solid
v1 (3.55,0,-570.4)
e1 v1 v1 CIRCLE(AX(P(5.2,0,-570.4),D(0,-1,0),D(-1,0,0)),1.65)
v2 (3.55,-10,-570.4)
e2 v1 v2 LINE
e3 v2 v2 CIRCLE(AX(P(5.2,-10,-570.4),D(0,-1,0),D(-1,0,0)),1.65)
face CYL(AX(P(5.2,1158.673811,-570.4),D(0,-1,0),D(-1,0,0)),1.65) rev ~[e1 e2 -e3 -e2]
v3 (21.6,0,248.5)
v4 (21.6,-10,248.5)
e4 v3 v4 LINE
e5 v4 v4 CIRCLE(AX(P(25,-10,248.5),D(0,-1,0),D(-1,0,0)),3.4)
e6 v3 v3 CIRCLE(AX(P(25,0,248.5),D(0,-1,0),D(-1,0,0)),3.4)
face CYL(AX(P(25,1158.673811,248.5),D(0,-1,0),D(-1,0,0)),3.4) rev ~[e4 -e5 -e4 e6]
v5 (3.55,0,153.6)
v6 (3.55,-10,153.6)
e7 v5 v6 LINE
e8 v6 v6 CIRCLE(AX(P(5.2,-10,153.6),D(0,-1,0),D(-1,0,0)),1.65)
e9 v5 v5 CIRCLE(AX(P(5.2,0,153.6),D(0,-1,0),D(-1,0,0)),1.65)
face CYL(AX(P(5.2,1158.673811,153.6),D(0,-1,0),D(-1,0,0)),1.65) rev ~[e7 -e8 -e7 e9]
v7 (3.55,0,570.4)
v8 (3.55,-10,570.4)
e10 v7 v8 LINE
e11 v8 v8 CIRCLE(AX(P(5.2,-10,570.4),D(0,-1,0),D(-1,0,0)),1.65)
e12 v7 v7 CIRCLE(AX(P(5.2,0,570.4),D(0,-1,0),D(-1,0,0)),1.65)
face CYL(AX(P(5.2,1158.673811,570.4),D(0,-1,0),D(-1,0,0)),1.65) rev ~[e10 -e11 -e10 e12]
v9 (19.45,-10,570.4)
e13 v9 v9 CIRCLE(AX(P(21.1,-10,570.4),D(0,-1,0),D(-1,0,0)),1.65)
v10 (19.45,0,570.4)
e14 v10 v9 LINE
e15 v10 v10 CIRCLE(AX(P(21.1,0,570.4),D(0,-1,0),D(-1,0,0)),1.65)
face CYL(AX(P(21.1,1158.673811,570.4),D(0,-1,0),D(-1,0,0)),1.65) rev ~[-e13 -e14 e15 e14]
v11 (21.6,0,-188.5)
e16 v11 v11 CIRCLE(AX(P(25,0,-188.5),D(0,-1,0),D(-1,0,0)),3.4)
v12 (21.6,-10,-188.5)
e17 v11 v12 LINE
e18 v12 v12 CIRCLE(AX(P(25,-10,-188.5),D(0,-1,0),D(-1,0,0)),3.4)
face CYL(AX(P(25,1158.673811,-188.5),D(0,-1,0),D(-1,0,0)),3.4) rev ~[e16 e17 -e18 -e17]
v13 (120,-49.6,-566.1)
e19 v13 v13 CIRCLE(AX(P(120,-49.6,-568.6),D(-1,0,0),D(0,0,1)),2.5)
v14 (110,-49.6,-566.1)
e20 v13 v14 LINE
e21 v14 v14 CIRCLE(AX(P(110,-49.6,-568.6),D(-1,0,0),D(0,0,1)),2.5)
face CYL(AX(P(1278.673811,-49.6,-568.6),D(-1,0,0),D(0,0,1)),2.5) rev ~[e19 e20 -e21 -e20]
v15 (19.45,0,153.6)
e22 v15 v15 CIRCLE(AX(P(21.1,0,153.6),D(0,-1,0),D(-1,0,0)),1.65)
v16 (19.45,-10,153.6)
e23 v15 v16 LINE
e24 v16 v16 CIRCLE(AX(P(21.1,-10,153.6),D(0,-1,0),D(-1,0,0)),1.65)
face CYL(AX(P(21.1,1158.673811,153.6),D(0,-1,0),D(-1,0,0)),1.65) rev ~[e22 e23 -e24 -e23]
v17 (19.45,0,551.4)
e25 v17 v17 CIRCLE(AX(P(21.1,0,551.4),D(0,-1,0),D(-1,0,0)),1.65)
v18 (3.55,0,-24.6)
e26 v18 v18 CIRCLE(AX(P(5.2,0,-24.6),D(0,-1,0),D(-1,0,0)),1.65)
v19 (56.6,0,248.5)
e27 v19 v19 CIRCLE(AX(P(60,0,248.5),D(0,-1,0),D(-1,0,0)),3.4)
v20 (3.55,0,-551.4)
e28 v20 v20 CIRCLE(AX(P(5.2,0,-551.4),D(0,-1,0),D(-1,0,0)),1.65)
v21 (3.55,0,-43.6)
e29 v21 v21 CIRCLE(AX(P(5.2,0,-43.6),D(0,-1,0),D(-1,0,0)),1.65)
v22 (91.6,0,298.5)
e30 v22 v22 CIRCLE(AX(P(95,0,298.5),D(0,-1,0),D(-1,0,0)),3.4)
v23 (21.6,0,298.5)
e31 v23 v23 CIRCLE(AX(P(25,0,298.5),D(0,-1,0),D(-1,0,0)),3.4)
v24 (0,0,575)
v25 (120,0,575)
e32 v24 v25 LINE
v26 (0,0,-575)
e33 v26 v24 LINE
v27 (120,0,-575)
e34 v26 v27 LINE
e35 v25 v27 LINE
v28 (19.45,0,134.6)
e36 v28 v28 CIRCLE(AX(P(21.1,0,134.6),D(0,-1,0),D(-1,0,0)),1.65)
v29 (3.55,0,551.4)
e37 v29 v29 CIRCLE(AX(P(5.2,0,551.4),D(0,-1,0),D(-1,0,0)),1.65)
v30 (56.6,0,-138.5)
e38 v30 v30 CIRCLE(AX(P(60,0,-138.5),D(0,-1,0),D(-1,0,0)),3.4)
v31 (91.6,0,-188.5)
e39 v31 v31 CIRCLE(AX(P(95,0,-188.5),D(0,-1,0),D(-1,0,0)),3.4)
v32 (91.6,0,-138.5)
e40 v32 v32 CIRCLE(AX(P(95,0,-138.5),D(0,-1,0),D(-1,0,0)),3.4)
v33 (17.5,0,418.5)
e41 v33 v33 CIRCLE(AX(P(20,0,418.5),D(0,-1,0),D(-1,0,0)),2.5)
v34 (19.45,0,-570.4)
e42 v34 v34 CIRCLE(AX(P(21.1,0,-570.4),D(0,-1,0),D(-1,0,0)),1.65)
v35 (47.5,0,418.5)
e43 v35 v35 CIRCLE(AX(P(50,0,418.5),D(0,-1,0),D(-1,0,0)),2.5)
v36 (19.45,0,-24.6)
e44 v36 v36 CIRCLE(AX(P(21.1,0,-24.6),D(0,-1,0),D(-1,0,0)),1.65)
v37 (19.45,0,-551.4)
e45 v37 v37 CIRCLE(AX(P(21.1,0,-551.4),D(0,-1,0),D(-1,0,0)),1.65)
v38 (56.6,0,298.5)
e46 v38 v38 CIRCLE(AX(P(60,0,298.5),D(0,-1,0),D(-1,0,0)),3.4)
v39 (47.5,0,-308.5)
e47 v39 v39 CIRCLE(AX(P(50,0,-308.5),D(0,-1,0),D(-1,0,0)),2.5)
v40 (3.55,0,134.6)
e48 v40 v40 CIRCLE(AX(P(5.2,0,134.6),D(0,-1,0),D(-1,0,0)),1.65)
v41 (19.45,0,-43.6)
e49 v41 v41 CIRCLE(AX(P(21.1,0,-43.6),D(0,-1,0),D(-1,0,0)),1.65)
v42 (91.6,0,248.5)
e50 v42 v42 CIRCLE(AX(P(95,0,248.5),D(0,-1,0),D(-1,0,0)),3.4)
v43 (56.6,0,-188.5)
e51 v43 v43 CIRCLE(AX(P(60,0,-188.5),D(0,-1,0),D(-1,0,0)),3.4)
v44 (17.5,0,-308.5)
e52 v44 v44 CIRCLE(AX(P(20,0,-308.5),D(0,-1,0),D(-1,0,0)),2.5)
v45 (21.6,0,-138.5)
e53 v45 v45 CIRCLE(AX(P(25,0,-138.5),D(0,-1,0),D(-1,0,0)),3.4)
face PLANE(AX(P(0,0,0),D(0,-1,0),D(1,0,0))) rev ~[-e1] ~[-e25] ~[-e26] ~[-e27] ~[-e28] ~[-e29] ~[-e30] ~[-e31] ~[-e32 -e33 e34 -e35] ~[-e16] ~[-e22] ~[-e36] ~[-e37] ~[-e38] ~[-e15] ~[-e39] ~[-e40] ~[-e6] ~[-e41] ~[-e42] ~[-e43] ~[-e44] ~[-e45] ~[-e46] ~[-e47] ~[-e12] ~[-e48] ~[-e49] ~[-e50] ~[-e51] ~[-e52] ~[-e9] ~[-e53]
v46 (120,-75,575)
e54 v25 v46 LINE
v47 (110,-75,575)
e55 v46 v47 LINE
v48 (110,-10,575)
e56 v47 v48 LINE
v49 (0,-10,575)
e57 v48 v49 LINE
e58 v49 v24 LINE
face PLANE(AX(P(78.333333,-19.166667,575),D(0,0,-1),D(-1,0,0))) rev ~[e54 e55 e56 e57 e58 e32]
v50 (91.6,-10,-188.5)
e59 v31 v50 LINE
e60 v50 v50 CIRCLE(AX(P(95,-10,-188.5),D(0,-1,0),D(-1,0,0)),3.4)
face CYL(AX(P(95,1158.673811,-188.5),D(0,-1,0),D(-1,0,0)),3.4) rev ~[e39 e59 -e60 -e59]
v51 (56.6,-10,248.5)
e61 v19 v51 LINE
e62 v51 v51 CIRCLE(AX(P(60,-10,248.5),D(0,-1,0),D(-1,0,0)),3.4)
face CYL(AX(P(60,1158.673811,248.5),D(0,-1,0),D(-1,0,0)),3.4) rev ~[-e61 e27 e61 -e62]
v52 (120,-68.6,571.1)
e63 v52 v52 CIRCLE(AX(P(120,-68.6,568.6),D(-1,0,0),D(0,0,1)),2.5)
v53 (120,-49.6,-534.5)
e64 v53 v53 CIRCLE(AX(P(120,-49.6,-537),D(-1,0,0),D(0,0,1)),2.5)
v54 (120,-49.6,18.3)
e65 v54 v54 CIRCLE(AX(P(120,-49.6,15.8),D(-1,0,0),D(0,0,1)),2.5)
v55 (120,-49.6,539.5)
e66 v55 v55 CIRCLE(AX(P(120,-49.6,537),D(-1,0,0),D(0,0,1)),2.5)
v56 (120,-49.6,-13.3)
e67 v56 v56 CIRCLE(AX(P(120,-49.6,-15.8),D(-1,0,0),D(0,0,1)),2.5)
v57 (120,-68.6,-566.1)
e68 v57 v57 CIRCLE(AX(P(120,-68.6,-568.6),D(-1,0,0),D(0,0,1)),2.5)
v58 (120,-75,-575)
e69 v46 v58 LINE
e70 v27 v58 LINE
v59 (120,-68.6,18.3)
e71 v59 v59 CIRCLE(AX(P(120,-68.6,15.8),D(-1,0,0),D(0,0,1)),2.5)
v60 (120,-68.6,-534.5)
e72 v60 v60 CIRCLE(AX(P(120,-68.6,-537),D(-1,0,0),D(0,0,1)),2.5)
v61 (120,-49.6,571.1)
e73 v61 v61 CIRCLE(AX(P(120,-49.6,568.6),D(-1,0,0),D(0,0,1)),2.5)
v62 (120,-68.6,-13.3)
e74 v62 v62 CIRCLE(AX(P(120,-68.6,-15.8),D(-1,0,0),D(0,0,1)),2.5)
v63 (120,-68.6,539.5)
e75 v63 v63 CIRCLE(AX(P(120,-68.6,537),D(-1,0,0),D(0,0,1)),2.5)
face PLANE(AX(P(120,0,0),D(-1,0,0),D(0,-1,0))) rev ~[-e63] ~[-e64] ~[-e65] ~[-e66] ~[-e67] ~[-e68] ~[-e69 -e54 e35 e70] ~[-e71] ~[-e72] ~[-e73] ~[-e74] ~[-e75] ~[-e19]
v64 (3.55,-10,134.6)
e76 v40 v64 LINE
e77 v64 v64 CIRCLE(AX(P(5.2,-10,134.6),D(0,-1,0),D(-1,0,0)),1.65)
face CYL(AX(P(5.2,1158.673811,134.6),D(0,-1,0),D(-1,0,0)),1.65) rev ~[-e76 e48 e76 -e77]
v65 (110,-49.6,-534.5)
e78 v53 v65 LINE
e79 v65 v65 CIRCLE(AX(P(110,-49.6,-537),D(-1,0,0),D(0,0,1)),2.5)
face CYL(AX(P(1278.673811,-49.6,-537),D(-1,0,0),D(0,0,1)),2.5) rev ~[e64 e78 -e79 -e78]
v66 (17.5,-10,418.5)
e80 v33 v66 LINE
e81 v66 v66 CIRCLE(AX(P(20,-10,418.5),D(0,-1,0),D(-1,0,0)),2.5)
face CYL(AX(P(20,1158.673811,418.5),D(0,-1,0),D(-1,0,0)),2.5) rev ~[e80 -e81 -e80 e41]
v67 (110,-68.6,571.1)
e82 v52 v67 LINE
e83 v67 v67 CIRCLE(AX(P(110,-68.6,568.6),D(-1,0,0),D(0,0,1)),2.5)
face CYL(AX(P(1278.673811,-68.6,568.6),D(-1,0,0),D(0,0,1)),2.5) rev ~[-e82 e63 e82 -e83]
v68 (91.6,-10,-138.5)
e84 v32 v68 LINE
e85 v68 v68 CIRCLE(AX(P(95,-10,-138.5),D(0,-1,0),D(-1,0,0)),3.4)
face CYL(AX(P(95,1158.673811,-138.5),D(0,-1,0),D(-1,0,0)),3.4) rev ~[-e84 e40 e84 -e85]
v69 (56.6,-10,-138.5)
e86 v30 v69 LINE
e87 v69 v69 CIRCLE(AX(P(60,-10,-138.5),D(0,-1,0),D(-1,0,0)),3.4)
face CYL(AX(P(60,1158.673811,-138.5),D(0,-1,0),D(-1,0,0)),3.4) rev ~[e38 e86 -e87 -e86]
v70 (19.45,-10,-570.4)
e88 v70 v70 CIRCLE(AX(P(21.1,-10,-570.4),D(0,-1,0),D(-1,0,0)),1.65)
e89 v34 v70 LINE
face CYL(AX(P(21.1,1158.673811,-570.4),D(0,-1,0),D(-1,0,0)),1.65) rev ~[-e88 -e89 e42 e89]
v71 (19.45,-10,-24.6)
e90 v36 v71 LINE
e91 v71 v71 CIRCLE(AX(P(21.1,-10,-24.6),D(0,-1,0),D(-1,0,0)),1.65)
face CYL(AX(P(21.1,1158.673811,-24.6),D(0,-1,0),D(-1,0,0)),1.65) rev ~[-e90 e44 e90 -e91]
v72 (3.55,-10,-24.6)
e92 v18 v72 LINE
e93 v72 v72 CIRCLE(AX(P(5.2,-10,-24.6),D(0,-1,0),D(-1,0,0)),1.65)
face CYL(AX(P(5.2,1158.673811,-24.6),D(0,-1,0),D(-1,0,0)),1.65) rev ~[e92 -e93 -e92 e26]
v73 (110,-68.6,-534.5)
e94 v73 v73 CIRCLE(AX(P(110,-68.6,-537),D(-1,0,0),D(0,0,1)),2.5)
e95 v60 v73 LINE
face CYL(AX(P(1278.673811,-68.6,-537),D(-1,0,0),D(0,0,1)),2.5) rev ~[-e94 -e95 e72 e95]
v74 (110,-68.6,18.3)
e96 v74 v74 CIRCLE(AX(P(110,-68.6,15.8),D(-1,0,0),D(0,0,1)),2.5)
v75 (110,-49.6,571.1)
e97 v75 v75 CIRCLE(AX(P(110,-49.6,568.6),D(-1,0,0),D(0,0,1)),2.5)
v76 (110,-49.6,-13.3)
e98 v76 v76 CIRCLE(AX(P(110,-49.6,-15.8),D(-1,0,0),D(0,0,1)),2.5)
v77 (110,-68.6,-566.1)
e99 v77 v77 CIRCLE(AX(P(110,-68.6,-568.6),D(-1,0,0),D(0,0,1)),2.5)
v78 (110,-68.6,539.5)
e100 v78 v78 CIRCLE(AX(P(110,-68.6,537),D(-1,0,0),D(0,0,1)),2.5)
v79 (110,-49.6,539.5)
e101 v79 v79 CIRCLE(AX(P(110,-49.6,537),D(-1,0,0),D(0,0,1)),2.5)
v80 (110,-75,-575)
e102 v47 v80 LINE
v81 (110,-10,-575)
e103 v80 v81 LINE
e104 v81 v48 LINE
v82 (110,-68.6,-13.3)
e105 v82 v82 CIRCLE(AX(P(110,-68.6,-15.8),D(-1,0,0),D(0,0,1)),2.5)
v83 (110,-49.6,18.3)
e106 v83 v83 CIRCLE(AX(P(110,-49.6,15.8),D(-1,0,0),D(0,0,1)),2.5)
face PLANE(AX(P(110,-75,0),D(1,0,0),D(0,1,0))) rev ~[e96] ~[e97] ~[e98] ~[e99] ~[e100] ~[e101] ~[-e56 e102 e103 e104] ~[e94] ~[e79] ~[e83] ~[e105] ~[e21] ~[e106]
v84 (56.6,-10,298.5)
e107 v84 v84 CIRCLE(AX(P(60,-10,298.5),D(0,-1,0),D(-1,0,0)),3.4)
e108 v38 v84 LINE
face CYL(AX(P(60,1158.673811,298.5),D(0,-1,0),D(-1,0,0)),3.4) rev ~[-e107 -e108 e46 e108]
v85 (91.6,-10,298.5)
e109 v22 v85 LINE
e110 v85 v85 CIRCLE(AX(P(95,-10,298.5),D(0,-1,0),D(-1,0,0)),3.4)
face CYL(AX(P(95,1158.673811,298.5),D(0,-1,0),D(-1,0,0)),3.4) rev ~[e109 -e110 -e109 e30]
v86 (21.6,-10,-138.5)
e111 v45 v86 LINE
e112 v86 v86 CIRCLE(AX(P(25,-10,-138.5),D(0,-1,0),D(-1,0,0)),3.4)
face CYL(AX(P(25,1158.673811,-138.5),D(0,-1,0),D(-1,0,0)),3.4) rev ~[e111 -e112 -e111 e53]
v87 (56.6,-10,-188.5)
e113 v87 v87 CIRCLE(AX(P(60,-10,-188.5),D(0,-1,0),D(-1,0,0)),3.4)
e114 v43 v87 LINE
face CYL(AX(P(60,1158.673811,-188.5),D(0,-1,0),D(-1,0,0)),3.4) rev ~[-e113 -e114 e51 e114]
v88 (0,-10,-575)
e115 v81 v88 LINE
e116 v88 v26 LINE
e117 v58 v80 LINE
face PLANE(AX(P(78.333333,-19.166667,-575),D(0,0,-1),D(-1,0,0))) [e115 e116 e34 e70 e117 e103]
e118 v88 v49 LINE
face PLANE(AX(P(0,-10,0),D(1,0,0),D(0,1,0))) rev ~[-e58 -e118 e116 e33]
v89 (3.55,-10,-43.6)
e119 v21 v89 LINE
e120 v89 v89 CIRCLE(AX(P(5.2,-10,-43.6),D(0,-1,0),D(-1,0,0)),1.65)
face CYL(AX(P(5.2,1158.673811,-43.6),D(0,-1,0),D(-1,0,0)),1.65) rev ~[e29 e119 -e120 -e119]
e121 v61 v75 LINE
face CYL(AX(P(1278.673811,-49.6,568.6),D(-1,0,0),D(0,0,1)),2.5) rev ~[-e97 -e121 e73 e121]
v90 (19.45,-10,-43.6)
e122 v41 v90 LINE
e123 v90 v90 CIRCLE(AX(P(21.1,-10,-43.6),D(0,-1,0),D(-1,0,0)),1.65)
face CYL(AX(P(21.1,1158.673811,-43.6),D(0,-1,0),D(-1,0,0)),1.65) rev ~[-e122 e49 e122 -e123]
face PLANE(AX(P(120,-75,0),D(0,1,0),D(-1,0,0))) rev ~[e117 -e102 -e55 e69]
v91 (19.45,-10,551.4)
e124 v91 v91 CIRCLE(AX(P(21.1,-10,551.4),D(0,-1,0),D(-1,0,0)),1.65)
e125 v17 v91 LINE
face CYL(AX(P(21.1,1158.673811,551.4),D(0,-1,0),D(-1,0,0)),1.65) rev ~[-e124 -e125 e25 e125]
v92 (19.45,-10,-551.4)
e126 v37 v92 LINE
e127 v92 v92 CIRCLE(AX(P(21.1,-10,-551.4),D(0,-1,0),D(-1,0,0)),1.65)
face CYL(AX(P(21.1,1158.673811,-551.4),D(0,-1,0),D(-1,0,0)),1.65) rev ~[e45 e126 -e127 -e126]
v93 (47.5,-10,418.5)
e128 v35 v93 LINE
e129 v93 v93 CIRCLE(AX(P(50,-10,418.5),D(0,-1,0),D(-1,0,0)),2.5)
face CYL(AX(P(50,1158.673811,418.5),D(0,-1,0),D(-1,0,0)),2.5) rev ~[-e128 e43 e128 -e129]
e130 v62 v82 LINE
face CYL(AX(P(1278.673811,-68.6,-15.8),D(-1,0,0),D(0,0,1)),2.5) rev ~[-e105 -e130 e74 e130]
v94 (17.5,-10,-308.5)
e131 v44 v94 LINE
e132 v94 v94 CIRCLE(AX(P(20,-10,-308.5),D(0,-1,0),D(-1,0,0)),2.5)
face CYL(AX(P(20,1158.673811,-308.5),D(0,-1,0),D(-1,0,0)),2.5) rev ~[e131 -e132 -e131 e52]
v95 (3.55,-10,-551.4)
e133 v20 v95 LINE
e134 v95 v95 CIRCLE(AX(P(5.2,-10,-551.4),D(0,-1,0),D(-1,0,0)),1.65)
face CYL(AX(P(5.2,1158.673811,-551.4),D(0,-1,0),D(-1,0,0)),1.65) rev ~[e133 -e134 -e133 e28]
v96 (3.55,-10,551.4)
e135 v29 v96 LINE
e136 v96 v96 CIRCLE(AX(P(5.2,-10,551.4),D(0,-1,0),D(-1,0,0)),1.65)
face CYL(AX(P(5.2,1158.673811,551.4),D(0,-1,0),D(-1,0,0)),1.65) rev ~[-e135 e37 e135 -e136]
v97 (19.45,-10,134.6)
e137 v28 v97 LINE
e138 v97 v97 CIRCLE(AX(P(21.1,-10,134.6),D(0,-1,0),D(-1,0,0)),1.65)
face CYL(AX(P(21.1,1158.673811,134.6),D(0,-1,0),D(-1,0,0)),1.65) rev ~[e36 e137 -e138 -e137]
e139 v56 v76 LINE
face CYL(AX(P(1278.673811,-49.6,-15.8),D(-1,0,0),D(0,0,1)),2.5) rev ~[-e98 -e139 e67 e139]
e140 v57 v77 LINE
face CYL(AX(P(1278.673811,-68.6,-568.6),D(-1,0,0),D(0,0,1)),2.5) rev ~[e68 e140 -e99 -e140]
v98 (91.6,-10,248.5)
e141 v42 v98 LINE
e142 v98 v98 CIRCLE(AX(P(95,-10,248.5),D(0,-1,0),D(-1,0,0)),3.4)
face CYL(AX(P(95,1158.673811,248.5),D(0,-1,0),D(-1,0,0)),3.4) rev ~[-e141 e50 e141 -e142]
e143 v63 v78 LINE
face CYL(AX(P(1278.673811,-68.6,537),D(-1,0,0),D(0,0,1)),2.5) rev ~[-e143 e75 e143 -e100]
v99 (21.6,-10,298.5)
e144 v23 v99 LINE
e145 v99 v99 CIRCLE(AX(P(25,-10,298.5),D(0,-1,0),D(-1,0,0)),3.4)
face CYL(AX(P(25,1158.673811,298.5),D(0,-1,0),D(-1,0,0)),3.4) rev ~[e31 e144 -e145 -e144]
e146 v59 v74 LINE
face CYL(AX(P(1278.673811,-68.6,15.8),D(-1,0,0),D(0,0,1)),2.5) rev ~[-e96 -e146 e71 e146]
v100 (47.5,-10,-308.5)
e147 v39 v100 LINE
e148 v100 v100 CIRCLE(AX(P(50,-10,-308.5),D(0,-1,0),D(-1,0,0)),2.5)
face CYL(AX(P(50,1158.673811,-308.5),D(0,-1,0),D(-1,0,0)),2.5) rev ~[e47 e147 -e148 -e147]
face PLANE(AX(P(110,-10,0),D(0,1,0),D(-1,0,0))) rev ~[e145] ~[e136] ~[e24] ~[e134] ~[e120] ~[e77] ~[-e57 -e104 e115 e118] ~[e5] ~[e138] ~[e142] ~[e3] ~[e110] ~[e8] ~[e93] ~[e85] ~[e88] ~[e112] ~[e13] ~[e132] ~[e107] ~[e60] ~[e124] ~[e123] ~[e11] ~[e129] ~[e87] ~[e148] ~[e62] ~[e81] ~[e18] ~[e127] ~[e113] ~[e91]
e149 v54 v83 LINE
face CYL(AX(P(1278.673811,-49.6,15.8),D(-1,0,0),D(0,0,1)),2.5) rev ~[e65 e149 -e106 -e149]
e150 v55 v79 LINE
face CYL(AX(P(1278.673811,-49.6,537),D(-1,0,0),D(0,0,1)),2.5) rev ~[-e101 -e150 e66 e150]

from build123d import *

# Parameters (mm, degrees)
EXTRUDE_1_DEPTH    = 575
HOLE_WIZARD_M4_1_D = 3.3
HOLE_WIZARD_M6_1_D = 5
HOLE_WIZARD_M8_1_D = 6.8
HOLE_WIZARD_M6_2_D = 5


with BuildPart() as part:
    # 草图1 → 凸台-拉伸1 (new, symmetric)
    with BuildSketch(Plane.XY):
        Polygon((0, 0), (120, 0), (120, -75), (110, -75), (110, -10), (0, -10), align=None)
    extrude(amount=EXTRUDE_1_DEPTH, both=True)

    # M4 螺纹孔1 (through all)
    with Locations(Plane(origin=(0, 0, 0), x_dir=(1, 0, 0), z_dir=(0, 1, 0))):
        with Locations((5.2, 43.6), (21.1, 43.6), (5.2, 24.6), (21.1, 24.6), (5.2, -134.6), (21.1, -134.6), (5.2, -153.6), (21.1, -153.6), (5.2, -551.4), (21.1, -551.4), (5.2, -570.4), (21.1, -570.4), (5.2, 570.4), (21.1, 570.4), (21.1, 551.4), (5.2, 551.4)):
            Hole(HOLE_WIZARD_M4_1_D / 2)

    # M6 螺纹孔1 (through all)
    with Locations(Plane(origin=(0, 0, 0), x_dir=(1, 0, 0), z_dir=(0, 1, 0))):
        with Locations((20, 308.5), (50, 308.5), (20, -418.5), (50, -418.5)):
            Hole(HOLE_WIZARD_M6_1_D / 2)

    # M8 螺纹孔1 (through all)
    with Locations(Plane(origin=(0, 0, 0), x_dir=(1, 0, 0), z_dir=(0, 1, 0))):
        with Locations((25, 188.5), (60, 188.5), (95, 188.5), (95, 138.5), (60, 138.5), (25, 138.5), (25, -248.5), (60, -248.5), (95, -248.5), (95, -298.5), (60, -298.5), (25, -298.5)):
            Hole(HOLE_WIZARD_M8_1_D / 2)

    # M6 螺纹孔2 (through all)
    with Locations(Plane(origin=(120, 0, 0), x_dir=(0, 0, -1), z_dir=(1, 0, 0))):
        with Locations((-568.6, -49.6), (-537, -49.6), (-537, -68.6), (-568.6, -68.6), (-15.8, -49.6), (15.8, -49.6), (15.8, -68.6), (-15.8, -68.6), (537, -49.6), (568.6, -49.6), (568.6, -68.6), (537, -68.6)):
            Hole(HOLE_WIZARD_M6_2_D / 2)


solid = part.part
